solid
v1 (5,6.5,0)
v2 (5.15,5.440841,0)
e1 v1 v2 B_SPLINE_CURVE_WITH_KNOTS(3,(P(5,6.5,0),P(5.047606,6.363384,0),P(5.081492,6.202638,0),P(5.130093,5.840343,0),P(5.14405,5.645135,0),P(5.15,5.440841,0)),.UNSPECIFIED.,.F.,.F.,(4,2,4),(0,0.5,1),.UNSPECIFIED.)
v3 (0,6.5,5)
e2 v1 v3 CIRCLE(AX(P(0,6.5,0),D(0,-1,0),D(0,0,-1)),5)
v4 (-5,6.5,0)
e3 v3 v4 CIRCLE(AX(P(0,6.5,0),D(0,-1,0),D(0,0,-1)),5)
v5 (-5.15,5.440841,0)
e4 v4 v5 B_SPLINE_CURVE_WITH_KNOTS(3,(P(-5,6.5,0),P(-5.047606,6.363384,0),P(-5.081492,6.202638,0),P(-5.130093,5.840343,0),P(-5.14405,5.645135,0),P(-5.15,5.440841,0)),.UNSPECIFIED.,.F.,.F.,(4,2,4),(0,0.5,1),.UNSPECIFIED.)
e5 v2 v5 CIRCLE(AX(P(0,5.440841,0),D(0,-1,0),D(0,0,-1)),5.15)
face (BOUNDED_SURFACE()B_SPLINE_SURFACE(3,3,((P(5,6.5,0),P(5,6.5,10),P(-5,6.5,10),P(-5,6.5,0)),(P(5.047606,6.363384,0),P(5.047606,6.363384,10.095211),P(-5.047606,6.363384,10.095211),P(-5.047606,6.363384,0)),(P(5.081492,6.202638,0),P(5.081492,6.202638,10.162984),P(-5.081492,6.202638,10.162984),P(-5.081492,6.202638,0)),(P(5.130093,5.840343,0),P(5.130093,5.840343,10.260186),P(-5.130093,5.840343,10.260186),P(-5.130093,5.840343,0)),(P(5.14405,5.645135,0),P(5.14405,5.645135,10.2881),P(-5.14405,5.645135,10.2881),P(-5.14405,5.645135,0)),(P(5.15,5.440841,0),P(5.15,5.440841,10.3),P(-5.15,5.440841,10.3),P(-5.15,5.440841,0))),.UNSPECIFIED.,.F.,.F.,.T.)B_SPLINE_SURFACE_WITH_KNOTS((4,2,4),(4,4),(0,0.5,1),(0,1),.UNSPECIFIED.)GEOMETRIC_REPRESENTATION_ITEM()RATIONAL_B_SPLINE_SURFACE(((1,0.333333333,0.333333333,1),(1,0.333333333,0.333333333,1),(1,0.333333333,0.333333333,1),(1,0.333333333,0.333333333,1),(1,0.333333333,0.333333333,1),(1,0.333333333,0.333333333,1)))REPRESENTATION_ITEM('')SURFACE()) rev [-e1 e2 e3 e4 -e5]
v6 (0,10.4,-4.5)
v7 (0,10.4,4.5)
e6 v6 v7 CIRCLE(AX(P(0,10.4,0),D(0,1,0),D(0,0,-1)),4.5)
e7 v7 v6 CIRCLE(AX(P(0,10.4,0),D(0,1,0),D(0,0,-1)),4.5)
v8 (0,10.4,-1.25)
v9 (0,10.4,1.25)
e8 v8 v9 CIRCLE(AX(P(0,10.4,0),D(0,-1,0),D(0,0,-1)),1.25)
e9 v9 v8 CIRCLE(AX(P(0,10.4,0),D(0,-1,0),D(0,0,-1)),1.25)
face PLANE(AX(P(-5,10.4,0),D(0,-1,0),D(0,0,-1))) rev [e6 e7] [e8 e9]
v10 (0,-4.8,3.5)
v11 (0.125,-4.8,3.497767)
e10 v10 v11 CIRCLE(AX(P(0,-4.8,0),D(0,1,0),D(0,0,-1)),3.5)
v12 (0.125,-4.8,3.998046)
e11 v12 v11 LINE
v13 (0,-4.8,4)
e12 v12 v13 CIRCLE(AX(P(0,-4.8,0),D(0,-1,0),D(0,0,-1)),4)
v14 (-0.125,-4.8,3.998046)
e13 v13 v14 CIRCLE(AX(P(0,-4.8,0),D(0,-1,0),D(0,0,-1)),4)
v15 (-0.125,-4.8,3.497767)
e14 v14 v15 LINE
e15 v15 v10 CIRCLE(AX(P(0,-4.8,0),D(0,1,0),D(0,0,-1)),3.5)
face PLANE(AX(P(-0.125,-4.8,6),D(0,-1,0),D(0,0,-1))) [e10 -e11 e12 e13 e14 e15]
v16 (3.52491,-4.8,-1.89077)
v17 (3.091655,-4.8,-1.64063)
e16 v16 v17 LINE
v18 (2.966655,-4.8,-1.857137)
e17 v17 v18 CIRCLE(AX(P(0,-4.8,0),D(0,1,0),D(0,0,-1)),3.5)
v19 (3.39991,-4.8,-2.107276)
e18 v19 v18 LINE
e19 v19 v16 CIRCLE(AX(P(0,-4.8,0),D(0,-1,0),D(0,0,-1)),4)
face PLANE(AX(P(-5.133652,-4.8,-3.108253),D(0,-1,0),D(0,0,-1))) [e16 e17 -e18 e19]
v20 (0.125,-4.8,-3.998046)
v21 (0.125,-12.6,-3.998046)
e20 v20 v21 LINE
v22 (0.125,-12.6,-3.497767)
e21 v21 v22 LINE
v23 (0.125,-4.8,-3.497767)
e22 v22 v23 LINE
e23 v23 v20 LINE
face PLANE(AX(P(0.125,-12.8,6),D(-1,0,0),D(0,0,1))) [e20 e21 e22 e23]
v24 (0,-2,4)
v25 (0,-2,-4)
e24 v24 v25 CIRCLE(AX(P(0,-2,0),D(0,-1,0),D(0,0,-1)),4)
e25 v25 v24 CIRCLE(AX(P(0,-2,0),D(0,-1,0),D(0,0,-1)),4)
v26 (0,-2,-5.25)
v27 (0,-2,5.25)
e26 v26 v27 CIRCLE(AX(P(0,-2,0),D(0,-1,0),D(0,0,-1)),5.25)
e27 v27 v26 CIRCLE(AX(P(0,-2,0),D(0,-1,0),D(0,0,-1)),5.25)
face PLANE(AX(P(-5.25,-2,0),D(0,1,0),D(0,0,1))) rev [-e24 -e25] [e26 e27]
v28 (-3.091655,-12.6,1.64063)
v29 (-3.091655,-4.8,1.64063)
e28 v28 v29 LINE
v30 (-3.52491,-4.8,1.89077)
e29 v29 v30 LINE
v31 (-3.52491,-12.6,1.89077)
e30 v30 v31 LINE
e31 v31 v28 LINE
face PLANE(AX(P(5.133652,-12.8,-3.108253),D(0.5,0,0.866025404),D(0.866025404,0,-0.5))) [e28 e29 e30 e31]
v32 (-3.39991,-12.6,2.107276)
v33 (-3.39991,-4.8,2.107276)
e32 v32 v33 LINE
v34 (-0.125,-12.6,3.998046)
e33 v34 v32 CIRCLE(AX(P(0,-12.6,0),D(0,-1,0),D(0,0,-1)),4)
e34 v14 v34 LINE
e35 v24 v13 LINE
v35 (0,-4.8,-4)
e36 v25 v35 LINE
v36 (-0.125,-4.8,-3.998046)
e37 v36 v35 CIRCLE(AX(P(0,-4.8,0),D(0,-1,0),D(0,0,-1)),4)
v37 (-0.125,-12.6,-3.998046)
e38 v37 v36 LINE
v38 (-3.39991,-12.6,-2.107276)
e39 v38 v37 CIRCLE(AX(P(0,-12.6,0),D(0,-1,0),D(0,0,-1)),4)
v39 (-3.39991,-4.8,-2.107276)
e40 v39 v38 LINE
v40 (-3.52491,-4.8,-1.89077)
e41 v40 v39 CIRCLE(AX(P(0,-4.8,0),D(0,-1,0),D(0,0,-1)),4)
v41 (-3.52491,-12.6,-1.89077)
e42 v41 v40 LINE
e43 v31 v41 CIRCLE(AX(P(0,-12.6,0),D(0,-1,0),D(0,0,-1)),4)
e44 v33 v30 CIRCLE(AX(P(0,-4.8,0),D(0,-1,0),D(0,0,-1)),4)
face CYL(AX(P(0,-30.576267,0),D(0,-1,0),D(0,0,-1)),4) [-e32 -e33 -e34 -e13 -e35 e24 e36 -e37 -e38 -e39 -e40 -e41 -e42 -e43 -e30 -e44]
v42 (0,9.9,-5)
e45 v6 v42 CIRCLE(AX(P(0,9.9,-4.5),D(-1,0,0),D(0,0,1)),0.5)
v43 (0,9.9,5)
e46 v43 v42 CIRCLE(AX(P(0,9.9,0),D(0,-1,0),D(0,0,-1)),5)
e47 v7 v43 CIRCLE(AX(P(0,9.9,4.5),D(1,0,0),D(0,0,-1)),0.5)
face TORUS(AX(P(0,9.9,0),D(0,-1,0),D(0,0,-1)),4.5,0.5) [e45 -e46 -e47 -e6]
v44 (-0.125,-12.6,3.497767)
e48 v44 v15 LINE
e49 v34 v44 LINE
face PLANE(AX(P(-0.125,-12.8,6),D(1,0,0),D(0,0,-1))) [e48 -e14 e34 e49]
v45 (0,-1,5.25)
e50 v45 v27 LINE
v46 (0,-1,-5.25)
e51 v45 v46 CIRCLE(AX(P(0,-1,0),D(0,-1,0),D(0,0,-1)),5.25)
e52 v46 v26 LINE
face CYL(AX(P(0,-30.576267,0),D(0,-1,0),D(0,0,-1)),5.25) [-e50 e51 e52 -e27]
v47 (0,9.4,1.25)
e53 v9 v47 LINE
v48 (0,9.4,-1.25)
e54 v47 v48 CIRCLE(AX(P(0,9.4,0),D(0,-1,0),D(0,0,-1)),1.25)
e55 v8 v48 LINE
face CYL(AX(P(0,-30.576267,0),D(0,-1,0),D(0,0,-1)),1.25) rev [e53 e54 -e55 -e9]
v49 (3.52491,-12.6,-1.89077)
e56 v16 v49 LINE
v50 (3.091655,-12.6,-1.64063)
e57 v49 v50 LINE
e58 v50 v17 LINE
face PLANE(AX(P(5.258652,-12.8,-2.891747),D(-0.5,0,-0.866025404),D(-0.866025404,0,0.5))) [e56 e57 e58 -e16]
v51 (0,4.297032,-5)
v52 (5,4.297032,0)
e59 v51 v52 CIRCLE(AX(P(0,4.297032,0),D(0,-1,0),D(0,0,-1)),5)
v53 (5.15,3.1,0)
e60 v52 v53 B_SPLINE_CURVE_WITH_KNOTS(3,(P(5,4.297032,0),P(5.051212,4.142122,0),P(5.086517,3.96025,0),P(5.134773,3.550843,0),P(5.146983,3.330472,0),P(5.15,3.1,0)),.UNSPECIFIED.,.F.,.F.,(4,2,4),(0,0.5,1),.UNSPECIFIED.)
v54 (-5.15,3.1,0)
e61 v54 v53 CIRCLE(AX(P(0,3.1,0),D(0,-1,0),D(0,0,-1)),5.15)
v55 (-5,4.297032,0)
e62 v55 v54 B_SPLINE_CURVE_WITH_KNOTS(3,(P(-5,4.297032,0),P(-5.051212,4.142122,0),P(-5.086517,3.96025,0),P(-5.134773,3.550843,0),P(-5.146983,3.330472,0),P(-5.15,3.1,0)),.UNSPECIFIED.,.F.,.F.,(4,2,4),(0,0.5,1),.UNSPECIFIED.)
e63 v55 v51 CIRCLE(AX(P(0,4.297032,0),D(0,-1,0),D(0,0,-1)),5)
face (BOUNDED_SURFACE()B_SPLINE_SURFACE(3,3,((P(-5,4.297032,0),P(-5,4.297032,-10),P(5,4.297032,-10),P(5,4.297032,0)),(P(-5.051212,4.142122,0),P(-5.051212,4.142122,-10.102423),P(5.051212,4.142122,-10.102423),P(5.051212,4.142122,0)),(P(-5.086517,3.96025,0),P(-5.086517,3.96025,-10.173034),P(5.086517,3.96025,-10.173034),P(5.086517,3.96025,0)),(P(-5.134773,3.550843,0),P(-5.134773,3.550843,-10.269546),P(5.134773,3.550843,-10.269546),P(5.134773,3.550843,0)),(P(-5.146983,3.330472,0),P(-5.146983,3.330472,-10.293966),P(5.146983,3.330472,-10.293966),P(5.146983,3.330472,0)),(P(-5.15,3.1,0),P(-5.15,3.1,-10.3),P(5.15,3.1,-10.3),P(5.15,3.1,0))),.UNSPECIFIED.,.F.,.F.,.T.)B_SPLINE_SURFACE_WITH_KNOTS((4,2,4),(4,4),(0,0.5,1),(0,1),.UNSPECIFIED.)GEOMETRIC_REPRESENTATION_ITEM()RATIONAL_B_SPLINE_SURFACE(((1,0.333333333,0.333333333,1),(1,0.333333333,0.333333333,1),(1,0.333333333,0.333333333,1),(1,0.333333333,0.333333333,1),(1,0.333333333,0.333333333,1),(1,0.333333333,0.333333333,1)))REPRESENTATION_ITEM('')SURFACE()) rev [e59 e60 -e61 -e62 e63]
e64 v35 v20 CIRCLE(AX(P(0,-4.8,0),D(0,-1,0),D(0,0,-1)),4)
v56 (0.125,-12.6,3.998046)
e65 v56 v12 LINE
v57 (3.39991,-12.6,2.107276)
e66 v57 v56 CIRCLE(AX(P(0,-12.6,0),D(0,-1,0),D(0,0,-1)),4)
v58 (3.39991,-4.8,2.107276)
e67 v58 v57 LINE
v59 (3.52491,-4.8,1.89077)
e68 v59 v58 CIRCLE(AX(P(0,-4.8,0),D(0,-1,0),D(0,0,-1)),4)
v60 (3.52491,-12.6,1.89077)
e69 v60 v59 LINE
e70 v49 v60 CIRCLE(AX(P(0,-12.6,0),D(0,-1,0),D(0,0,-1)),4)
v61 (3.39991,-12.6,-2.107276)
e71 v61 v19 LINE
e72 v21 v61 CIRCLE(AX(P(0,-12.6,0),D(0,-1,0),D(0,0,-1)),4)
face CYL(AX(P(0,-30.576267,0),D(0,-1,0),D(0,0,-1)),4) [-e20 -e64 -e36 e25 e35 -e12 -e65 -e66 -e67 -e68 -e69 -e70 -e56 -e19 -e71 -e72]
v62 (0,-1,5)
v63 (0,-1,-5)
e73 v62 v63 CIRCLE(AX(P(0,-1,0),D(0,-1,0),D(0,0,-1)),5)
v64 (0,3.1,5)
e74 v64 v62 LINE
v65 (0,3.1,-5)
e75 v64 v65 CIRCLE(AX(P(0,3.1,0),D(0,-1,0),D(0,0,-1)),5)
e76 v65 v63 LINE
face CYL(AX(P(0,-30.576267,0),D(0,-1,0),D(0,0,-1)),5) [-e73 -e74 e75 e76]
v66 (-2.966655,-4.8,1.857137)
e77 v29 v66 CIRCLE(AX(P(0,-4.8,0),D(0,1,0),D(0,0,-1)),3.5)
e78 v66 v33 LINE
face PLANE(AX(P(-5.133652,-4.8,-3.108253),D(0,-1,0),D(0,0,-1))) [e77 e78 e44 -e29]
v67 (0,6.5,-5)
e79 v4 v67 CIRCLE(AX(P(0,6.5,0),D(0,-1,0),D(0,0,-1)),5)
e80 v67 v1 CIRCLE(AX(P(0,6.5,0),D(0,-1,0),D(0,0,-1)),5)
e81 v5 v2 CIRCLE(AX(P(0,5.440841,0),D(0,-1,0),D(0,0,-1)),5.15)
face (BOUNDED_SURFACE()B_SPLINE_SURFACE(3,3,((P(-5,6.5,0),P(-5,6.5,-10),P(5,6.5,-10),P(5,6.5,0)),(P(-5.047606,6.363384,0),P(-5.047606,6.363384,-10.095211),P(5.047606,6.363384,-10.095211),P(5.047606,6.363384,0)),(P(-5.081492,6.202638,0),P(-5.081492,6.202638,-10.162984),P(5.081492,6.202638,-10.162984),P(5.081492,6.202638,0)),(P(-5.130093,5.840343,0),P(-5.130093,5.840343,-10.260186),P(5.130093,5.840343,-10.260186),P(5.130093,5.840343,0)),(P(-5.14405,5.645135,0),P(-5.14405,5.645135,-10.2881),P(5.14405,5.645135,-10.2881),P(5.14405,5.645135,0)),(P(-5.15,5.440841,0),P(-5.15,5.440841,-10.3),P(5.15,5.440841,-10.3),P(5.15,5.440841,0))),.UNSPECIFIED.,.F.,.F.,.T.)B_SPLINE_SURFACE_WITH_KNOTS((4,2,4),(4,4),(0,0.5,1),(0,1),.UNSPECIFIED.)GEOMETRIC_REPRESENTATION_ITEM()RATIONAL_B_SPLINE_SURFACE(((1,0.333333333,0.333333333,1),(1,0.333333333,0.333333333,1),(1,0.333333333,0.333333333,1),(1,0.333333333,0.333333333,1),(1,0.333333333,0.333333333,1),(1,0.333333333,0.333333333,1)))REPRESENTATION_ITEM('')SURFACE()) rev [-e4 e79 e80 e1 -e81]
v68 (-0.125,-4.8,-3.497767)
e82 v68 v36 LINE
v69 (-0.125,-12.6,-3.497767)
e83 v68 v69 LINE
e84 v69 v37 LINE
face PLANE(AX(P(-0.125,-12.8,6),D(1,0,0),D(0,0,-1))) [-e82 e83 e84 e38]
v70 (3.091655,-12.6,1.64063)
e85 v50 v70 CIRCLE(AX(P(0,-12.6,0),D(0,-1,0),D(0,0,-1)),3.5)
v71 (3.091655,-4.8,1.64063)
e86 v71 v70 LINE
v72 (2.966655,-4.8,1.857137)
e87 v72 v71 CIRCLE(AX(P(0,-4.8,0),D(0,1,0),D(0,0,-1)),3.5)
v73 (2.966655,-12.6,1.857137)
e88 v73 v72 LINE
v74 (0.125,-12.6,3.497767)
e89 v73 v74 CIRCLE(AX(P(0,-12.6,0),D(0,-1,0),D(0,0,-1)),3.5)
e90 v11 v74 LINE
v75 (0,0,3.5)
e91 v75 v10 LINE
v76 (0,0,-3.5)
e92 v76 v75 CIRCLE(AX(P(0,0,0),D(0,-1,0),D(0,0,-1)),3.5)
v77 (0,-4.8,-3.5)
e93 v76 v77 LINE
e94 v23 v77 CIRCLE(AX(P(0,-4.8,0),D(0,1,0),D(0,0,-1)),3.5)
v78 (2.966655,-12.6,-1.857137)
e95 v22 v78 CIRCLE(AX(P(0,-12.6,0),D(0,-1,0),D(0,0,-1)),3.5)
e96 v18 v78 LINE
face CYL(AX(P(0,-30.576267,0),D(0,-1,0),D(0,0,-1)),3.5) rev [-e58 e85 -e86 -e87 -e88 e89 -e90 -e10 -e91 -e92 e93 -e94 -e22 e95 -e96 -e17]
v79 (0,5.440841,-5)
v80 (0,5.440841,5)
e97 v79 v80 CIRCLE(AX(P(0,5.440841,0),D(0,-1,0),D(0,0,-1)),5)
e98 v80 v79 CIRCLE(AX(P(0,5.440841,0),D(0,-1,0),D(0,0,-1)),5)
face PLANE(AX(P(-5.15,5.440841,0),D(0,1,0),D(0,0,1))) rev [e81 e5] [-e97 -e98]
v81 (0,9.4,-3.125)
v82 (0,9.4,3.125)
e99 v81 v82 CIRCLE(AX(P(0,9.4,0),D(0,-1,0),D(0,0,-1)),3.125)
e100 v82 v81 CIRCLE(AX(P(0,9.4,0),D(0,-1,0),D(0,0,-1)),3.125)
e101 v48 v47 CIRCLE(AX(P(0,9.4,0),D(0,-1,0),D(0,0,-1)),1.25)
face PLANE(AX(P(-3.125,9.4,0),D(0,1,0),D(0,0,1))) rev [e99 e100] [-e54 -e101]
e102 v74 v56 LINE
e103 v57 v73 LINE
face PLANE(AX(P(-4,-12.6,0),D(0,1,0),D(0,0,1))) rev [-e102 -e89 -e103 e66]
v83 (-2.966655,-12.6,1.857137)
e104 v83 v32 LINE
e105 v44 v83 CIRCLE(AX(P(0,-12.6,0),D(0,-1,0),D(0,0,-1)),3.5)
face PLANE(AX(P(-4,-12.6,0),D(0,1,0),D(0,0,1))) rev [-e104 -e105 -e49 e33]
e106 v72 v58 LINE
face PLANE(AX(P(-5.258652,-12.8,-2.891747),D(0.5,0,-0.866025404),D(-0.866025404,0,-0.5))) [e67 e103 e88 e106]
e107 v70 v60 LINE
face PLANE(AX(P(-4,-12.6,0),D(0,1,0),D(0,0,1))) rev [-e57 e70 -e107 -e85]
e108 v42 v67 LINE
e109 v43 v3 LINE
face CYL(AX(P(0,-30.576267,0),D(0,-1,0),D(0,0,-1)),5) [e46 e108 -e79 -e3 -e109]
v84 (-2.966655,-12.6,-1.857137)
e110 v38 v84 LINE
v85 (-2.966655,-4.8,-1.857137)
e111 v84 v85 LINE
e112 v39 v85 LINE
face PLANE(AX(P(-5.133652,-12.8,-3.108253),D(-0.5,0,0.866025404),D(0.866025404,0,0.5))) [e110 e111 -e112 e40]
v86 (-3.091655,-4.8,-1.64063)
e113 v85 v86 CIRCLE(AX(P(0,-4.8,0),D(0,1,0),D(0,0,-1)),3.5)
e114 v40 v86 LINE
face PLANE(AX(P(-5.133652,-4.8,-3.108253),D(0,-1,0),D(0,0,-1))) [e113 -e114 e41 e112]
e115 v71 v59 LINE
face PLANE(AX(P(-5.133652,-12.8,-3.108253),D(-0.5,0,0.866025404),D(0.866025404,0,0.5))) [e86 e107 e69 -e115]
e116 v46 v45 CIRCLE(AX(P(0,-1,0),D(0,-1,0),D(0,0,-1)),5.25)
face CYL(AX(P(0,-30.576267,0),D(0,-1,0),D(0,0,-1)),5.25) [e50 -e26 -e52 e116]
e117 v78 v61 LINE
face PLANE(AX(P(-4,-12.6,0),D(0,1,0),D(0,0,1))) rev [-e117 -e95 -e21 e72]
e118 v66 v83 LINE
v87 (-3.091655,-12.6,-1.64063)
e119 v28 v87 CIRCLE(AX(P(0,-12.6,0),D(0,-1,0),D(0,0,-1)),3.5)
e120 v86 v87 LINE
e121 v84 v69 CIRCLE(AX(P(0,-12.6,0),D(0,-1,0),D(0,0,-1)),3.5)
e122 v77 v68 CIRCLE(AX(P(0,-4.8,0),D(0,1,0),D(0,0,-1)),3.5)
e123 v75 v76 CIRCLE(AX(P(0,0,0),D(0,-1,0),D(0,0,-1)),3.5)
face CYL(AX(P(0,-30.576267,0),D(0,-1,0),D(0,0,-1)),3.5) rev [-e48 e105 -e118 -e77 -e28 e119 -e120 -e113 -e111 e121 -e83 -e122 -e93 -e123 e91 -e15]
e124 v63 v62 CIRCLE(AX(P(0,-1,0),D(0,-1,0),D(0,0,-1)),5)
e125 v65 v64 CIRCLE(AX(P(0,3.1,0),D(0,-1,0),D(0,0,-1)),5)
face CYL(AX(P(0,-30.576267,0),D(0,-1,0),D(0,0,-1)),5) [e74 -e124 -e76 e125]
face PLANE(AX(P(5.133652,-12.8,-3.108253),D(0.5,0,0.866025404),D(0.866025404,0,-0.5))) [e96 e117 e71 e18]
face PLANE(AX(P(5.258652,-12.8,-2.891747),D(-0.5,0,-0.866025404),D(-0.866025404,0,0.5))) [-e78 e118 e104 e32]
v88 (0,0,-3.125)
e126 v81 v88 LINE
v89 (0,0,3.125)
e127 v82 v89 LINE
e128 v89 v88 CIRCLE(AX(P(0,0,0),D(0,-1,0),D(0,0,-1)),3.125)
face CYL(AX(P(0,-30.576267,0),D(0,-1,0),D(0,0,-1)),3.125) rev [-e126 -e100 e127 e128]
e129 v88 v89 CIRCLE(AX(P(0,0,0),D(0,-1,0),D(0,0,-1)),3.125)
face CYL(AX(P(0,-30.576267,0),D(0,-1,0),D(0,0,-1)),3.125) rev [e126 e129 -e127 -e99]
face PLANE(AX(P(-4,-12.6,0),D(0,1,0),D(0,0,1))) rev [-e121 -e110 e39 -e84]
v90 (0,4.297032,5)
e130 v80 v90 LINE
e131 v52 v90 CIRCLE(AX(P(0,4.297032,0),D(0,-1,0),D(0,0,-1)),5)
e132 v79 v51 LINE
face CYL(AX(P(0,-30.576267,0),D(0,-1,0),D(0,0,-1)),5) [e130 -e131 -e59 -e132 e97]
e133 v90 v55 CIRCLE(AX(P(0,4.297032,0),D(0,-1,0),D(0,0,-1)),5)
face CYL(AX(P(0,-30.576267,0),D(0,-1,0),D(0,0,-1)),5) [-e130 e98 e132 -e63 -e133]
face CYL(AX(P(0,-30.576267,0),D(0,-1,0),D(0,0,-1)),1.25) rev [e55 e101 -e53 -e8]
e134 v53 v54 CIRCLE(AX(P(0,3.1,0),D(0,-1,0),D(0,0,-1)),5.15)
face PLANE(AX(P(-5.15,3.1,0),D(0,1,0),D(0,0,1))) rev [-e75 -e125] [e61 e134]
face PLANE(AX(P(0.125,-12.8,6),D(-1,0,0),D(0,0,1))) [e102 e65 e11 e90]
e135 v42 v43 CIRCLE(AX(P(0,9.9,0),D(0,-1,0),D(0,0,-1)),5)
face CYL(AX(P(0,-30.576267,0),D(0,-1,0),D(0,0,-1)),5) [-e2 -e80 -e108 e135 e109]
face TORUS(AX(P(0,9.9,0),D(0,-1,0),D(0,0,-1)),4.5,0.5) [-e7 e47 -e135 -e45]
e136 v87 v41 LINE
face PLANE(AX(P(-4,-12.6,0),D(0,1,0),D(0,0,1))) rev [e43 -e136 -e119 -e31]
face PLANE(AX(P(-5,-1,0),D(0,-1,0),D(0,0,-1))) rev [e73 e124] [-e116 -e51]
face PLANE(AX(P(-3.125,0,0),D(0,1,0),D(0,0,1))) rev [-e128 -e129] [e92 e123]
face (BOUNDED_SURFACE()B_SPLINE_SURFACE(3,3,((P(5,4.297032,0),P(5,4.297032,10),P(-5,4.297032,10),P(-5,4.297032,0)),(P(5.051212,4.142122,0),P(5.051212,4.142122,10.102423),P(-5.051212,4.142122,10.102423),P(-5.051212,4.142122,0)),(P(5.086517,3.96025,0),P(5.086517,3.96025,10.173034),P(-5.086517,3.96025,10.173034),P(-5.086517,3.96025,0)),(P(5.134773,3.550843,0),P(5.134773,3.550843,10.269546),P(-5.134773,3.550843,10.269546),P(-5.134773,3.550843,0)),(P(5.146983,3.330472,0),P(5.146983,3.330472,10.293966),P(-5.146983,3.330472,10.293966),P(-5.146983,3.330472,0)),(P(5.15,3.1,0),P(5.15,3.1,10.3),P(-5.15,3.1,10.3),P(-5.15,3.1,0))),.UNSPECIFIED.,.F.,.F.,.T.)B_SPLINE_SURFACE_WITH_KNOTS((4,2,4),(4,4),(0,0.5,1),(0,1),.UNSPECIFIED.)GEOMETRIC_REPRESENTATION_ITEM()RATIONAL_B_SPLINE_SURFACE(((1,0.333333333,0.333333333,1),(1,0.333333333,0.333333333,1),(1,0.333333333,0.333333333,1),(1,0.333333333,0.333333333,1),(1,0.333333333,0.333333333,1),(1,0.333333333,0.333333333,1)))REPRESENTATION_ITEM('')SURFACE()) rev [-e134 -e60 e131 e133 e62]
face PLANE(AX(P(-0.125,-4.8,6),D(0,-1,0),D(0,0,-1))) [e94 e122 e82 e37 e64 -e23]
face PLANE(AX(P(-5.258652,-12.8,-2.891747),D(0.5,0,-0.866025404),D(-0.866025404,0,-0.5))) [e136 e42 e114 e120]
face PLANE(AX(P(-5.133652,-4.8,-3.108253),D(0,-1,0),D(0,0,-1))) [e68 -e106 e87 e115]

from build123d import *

# Parameters (mm, degrees)
FILLET1_R          = 0.5
SKETCH8_W          = 0.25
SKETCH8_H          = 8
CUT_EXTRUDE1_DEPTH = 6
CIRPATTERN1_COUNT  = 3


with BuildPart() as part:
    # Sketch1 → Revolve1 (revolve)
    with BuildSketch(Plane.XY, mode=Mode.PRIVATE) as revolve1_sk:
        with BuildLine():
            Line((-5, 3.1), (-5, -1))
            Line((-5, -1), (-5.25, -1))
            Line((-5.25, -1), (-5.25, -2))
            Line((-5.25, -2), (-4, -2))
            Line((-4, -2), (-4, -12.6))
            Line((-4, -12.6), (-3.5, -12.6))
            Line((-3.5, -12.6), (-3.5, 0))
            Line((-3.5, 0), (-3.125, 0))
            Line((-3.125, 0), (-3.125, 9.4))
            Line((-3.125, 9.4), (-1.25, 9.4))
            Line((-1.25, 9.4), (-1.25, 10.4))
            Line((-1.25, 10.4), (-5, 10.4))
            Line((-5, 10.4), (-5, 6.5))
            add(Edge.make_bspline(
                [(-5, 6.5), (-5.047605665, 6.363384357), (-5.0814919, 6.202637521), (-5.130093219, 5.840342723), (-5.144049999, 5.645135031), (-5.15, 5.440840859)],
                knots=[0, 0, 0, 0, 0.5, 0.5, 1, 1, 1, 1], degree=3))
            Line((-5.15, 5.440840859), (-5, 5.440840859))
            Line((-5, 5.440840859), (-5, 4.297032053))
            add(Edge.make_bspline(
                [(-5, 4.297032053), (-5.05121173, 4.142122175), (-5.086517142, 3.960249608), (-5.134772947, 3.550843087), (-5.146982855, 3.330472207), (-5.15, 3.1)],
                knots=[0, 0, 0, 0, 0.5, 0.5, 1, 1, 1, 1], degree=3))
            Line((-5.15, 3.1), (-5, 3.1))
        make_face()
    revolve(revolve1_sk.sketch.rotate(Axis((0, -30.576267402, 0), (0, 1, 0)), 270), axis=Axis((0, -30.576267402, 0), (0, 1, 0)))

    # Fillet1
    fillet1_edges = [part.edges().sort_by_distance(p)[0] for p in [
        (0, 10.4, 5),
    ]]
    fillet(fillet1_edges, radius=FILLET1_R)

    # Sketch8 → Cut-Extrude1 (cut, symmetric)
    with BuildSketch(Plane.XY):
        with Locations((0, -8.8)):
            Rectangle(SKETCH8_W, SKETCH8_H)
    cut_extrude1 = extrude(amount=CUT_EXTRUDE1_DEPTH, both=True, mode=Mode.SUBTRACT)

    # CirPattern1: Cut-Extrude1 ×3 about axis
    cirpattern1_axis = Axis((0, 0, 0), (0, 1, 0))
    for i in range(1, CIRPATTERN1_COUNT):
        add(cut_extrude1.rotate(cirpattern1_axis, i * 360 / CIRPATTERN1_COUNT), mode=Mode.SUBTRACT)


solid = part.part
